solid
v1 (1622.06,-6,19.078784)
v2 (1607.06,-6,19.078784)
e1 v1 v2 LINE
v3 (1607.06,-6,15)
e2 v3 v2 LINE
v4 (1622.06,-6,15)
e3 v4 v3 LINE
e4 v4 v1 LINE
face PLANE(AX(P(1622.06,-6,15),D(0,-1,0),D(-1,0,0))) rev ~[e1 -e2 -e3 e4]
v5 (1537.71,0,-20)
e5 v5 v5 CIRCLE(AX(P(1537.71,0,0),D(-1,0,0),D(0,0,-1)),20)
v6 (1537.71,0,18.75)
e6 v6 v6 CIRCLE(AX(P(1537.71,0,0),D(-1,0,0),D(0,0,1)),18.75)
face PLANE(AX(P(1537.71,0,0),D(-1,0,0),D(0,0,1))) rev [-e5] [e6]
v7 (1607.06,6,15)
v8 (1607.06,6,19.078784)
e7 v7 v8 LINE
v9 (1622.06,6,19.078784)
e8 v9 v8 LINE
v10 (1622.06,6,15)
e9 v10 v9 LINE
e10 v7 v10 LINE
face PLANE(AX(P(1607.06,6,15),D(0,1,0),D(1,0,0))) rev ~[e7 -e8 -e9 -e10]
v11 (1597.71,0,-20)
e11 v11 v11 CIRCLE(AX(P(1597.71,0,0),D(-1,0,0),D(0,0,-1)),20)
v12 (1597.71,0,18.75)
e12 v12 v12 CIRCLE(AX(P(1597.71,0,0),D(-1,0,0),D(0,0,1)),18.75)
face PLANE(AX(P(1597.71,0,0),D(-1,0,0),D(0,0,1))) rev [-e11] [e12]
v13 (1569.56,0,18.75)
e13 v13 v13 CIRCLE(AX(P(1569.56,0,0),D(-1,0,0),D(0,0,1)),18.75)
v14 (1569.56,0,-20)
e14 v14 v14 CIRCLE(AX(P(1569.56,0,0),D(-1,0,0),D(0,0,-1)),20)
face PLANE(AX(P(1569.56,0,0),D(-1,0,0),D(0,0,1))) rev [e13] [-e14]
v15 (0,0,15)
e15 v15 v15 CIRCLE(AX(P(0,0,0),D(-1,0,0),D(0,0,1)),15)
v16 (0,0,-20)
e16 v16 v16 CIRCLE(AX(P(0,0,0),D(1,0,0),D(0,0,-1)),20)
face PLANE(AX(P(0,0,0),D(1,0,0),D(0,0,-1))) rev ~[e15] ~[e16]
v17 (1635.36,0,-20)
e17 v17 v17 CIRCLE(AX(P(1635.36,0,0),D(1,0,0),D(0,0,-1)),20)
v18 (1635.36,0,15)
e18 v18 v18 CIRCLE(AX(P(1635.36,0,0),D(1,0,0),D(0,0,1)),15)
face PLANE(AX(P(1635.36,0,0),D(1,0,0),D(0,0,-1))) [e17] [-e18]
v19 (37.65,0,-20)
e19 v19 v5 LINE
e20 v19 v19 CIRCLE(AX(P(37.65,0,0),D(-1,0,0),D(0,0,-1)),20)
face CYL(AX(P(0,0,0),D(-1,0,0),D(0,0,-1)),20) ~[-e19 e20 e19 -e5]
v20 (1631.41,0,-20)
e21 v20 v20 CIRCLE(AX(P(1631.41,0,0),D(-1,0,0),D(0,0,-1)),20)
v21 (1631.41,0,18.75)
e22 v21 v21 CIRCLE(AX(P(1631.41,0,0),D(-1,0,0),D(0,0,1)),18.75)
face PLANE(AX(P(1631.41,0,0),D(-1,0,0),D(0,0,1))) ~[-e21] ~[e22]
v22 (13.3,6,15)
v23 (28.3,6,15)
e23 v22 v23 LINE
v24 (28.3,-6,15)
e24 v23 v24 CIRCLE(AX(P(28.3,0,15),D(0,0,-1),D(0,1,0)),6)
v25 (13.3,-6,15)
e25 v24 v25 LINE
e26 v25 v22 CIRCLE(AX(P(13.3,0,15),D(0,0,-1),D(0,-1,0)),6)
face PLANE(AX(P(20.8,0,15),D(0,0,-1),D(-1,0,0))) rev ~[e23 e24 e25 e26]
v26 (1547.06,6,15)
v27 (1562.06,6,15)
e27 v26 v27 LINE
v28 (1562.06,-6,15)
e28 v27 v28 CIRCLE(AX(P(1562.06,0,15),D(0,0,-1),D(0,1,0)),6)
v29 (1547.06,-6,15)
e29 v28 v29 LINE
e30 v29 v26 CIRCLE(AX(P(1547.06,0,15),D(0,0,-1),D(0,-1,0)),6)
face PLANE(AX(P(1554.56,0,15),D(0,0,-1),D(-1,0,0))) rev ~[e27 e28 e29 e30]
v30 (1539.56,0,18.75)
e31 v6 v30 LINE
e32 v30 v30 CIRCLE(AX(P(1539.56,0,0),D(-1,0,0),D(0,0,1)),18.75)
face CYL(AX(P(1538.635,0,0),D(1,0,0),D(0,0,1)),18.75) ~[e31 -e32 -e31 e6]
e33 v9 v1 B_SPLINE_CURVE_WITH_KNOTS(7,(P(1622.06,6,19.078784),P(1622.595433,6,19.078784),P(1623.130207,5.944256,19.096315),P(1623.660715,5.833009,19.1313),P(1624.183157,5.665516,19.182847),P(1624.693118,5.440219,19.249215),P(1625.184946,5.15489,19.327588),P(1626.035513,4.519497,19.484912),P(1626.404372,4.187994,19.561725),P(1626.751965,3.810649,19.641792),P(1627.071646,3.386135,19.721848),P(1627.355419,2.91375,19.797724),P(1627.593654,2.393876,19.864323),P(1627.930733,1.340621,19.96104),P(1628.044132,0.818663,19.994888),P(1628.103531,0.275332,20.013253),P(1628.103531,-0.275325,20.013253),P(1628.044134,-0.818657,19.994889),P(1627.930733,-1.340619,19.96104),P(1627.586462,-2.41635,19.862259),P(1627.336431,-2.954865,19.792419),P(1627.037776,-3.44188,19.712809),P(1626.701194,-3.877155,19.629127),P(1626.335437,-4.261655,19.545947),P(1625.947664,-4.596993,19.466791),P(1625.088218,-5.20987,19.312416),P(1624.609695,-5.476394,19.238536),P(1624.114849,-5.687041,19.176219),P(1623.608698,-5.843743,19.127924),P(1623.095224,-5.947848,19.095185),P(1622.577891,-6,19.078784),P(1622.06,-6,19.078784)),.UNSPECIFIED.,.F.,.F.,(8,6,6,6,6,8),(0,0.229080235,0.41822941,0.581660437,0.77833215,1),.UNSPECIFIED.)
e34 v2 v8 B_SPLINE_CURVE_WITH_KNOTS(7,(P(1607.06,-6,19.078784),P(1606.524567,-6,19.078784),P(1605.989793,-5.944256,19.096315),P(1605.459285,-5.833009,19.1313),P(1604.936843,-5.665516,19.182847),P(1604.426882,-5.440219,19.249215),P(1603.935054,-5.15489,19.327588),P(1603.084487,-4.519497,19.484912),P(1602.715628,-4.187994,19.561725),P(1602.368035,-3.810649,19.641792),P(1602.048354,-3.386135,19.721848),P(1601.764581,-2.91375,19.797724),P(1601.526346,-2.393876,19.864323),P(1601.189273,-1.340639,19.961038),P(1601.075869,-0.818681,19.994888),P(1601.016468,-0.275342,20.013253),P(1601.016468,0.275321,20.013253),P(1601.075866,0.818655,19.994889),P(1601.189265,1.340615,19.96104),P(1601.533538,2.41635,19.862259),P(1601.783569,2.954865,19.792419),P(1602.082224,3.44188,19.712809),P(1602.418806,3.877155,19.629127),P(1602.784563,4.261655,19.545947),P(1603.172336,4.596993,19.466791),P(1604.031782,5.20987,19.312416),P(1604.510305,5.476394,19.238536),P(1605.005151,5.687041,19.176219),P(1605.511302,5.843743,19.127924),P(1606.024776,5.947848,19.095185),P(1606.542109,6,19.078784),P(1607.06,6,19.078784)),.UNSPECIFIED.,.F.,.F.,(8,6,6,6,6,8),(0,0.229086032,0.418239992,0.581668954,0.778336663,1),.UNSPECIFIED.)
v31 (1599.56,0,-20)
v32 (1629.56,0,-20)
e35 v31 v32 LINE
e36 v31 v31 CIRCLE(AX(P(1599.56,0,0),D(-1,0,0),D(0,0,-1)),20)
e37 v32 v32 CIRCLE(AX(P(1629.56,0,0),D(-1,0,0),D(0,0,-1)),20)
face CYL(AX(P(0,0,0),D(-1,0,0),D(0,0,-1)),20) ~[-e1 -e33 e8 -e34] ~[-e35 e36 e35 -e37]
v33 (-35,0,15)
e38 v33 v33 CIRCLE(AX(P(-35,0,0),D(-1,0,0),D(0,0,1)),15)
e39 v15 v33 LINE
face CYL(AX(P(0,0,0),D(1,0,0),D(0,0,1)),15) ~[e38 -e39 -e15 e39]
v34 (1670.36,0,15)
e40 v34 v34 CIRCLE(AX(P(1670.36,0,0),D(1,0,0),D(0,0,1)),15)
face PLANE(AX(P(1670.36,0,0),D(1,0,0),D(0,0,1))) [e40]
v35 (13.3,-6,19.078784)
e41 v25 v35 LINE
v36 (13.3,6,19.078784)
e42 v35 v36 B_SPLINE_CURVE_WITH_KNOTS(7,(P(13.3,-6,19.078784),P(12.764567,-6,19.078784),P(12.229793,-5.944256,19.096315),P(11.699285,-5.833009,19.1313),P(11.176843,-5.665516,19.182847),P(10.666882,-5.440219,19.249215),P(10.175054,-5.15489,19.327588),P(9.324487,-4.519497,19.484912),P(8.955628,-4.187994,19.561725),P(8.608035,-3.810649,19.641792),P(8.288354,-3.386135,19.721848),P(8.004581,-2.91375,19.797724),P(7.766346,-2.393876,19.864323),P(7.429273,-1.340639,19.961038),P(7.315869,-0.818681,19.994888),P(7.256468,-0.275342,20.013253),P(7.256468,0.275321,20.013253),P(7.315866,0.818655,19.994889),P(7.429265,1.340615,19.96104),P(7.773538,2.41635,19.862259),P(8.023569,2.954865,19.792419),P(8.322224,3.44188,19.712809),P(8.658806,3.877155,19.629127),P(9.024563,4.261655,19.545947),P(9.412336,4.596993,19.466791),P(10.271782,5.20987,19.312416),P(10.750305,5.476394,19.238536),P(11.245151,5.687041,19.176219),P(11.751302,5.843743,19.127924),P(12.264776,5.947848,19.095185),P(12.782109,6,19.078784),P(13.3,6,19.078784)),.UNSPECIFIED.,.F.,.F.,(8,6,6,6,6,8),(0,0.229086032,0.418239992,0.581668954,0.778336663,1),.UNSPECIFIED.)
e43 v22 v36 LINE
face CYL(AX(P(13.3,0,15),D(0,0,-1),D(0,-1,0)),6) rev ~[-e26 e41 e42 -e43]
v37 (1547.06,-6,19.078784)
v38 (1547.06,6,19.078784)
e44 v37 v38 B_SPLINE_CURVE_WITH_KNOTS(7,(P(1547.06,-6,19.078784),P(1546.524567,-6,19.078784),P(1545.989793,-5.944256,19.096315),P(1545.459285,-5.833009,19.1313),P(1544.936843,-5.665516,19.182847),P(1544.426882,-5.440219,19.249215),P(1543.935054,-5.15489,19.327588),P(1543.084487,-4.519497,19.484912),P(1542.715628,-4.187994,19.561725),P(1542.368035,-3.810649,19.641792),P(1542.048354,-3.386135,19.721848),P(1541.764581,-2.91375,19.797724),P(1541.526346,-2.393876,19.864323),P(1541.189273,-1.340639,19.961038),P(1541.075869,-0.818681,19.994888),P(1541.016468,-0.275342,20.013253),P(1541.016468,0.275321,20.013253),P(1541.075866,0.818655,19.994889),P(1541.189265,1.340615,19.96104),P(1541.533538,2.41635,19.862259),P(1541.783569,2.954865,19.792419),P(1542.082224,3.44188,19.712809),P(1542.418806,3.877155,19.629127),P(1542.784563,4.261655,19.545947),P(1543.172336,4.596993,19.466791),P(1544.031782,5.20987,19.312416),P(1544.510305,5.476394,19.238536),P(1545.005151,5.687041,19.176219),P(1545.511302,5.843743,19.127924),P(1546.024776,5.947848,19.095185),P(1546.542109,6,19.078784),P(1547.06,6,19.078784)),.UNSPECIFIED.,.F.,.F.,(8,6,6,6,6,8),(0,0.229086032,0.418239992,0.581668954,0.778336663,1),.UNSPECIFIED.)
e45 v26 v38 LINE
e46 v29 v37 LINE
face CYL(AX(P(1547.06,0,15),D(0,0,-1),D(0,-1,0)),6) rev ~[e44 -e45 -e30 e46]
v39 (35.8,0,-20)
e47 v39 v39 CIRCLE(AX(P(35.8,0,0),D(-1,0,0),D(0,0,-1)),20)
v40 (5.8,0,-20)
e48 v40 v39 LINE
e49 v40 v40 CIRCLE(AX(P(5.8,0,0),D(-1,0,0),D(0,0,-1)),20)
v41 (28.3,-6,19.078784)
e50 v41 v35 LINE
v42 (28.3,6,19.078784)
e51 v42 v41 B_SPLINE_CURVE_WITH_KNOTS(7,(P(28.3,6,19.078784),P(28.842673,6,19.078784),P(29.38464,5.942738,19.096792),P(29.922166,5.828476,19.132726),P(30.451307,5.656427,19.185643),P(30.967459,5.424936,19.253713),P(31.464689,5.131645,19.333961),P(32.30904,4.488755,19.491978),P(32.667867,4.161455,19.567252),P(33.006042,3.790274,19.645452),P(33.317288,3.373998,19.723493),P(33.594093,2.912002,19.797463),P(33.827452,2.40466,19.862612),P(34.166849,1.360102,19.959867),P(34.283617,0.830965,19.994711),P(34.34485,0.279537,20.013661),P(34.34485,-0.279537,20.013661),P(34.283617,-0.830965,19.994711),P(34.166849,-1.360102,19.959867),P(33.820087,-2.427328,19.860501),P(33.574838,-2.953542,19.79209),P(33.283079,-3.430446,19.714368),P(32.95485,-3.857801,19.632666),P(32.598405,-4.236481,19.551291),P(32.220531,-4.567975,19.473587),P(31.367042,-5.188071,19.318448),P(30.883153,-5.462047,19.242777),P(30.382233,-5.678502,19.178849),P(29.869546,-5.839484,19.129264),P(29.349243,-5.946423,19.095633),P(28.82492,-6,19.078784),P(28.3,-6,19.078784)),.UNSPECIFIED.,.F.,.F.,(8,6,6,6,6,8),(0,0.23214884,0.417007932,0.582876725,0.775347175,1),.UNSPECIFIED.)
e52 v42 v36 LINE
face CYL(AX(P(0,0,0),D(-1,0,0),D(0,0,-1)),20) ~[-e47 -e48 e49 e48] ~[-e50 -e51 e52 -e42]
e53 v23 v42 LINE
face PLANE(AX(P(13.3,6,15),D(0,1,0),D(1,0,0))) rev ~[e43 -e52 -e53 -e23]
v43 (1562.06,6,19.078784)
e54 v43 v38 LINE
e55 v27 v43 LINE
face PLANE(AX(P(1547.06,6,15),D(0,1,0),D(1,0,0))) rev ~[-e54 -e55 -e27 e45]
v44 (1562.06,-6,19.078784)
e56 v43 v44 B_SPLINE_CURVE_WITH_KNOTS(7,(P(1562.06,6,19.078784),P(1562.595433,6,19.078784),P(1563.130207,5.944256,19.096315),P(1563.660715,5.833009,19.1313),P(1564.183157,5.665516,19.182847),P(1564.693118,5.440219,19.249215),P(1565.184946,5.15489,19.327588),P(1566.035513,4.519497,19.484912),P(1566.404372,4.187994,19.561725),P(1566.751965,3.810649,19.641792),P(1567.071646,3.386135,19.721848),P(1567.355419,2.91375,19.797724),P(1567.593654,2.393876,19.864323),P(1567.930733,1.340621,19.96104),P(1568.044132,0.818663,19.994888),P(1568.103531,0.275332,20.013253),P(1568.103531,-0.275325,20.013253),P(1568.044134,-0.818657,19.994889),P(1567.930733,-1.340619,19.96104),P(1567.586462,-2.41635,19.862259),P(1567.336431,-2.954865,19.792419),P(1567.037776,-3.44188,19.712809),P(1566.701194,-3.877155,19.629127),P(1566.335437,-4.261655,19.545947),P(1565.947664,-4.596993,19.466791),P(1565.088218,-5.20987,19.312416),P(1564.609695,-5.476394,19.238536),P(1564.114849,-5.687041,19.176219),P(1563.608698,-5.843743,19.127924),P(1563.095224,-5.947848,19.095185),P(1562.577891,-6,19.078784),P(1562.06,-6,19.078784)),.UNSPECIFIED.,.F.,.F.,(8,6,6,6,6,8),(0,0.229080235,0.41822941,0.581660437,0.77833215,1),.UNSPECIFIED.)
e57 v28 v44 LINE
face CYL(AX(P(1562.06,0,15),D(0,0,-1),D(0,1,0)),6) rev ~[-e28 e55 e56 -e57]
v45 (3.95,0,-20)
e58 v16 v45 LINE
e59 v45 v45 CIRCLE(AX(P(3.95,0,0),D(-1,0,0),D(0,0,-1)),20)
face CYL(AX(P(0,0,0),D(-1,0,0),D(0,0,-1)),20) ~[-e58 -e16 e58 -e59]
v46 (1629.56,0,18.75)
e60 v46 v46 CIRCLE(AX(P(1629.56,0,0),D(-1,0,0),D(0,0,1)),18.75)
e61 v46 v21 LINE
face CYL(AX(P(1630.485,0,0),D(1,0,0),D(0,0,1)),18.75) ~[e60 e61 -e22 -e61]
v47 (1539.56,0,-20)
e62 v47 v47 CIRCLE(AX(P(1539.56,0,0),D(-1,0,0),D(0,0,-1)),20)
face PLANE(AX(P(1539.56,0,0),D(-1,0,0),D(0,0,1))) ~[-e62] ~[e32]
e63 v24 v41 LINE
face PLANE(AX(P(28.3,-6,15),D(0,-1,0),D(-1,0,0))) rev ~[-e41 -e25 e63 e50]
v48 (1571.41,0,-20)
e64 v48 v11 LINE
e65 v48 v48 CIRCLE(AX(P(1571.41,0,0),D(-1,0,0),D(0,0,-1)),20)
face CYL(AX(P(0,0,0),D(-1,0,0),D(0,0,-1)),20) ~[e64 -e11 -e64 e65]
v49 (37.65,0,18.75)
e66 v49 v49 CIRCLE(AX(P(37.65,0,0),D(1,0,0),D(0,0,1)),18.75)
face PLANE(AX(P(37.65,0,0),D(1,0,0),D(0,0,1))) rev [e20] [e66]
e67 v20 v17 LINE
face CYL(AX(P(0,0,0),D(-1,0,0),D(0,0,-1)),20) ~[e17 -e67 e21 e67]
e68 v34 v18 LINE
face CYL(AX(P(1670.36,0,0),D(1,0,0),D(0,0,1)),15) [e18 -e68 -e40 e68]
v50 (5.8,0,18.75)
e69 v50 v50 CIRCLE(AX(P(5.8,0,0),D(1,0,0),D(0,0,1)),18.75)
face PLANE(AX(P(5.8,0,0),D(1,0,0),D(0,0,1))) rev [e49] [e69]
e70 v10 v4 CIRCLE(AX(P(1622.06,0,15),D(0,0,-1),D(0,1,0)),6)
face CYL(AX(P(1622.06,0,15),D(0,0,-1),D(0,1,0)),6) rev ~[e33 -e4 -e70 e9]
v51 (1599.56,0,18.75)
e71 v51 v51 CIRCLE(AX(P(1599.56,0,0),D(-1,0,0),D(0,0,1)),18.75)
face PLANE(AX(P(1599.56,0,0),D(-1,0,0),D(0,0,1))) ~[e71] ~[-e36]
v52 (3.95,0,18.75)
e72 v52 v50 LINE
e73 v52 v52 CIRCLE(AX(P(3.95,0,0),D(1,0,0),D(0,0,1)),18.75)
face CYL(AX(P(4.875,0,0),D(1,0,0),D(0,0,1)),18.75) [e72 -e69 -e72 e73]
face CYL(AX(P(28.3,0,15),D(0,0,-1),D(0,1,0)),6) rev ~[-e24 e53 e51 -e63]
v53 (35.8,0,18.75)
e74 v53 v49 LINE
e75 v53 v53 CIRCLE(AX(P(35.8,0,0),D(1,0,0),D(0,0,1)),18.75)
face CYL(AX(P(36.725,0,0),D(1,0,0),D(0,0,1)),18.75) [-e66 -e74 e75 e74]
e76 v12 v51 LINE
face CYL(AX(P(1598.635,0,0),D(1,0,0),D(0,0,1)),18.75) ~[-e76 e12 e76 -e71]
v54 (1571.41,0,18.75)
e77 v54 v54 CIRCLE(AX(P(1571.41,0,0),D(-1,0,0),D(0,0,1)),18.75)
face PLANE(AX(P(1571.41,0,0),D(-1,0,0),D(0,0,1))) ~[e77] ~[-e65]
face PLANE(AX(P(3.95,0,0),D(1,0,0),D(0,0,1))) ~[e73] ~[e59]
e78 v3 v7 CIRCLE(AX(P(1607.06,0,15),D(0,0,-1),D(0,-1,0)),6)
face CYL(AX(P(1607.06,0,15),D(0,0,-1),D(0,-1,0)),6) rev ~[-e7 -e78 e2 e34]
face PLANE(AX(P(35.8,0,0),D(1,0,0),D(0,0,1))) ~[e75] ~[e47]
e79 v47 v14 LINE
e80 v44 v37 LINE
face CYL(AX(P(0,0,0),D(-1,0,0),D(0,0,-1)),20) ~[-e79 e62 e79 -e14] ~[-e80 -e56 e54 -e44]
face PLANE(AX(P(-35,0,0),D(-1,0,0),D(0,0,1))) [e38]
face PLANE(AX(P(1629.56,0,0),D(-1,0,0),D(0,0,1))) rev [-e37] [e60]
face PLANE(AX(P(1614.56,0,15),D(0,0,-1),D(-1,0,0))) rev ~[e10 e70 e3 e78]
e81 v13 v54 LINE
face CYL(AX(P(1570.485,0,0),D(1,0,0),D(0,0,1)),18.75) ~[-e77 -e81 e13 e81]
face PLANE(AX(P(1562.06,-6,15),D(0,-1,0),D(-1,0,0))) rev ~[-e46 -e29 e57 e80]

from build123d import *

# Parameters (mm, degrees)
SKETCH_1_R             = 20
EXTRUDE_1_DEPTH        = 1635.36
SKETCH_2_R             = 15
EXTRUDE_2_DEPTH        = 35
EXTRUDE_START          = 35
SKETCH_3_R             = 15
EXTRUDE_3_DEPTH        = 35
CUT_EXTRUDE_1_DEPTH    = 1671.846351284
SKETCH_5_W             = 1.85
SKETCH_5_H             = 1.25
SKETCH_7_W             = 1.85
SKETCH_7_H             = 1.25
PATTERN_LINEAR_2_COUNT = 2
PATTERN_LINEAR_2_PITCH = 60


with BuildPart() as part:
    # 草图1 → 凸台-拉伸1 (new body)
    with BuildSketch(Plane(origin=(0, 0, 0), x_dir=(0, 0, -1), z_dir=(1, 0, 0))):
        Circle(SKETCH_1_R)
    extrude(amount=EXTRUDE_1_DEPTH)

    # 草图2 → 凸台-拉伸2 (add)
    with BuildSketch(Plane.ZY):
        Circle(SKETCH_2_R)
    extrude(amount=EXTRUDE_2_DEPTH)

    # 草图3 → 凸台-拉伸3 (add)
    with BuildSketch(Plane(origin=(1635.36, 0, 0), x_dir=(0, 0, -1), z_dir=(1, 0, 0)).offset(EXTRUDE_START)):
        with Locations(Location((0, 0, 0), (0, 0, 180))):
            Circle(SKETCH_3_R)
    extrude(amount=-EXTRUDE_3_DEPTH)

    # 草图4 → 切除-拉伸1 (cut, through all)
    with BuildSketch(Plane.XY.offset(15)):
        with BuildLine():
            Line((13.3, 6), (28.3, 6))
            ThreePointArc((28.3, 6), (34.3, 0), (28.3, -6))
            Line((28.3, -6), (13.3, -6))
            ThreePointArc((13.3, -6), (7.3, 0), (13.3, 6))
        make_face()
        with BuildLine():
            Line((1622.06, -6), (1607.06, -6))
            ThreePointArc((1607.06, -6), (1601.06, 0), (1607.06, 6))
            Line((1607.06, 6), (1622.06, 6))
            ThreePointArc((1622.06, 6), (1628.06, 0), (1622.06, -6))
        make_face()
        with BuildLine():
            Line((1562.06, -6), (1547.06, -6))
            ThreePointArc((1547.06, -6), (1541.06, 0), (1547.06, 6))
            Line((1547.06, 6), (1562.06, 6))
            ThreePointArc((1562.06, 6), (1568.06, 0), (1562.06, -6))
        make_face()
    extrude(amount=CUT_EXTRUDE_1_DEPTH, mode=Mode.SUBTRACT)

    # 草图5 → 切除-旋转1 (revolve, cut)
    with BuildSketch(Plane.XY, mode=Mode.PRIVATE) as cut_revolve_1_sk:
        with Locations((4.875, 19.375)):
            Rectangle(SKETCH_5_W, SKETCH_5_H)
        with Locations((36.725, 19.375)):
            Rectangle(SKETCH_5_W, SKETCH_5_H)
    revolve(cut_revolve_1_sk.sketch.rotate(Axis((0, 0, 0), (1, 0, 0)), 90), axis=Axis((0, 0, 0), (1, 0, 0)), mode=Mode.SUBTRACT)

    # 草图7 → 切除-旋转2 (revolve, cut)
    with BuildSketch(Plane.XY, mode=Mode.PRIVATE) as cut_revolve_2_sk:
        with Locations((1598.635, 19.375)):
            Rectangle(SKETCH_7_W, SKETCH_7_H)
        with Locations((1630.485, 19.375)):
            Rectangle(SKETCH_7_W, SKETCH_7_H)
    cut_revolve_2 = revolve(cut_revolve_2_sk.sketch.rotate(Axis((1670.36, 0, 0), (-1, 0, 0)), 270), axis=Axis((1670.36, 0, 0), (-1, 0, 0)), mode=Mode.SUBTRACT)

    # 阵列(线性)2: 切除-旋转2 ×2
    with Locations(*[(-i * PATTERN_LINEAR_2_PITCH, 0, 0) for i in range(1, PATTERN_LINEAR_2_COUNT)]):
        add(cut_revolve_2, mode=Mode.SUBTRACT)


solid = part.part
